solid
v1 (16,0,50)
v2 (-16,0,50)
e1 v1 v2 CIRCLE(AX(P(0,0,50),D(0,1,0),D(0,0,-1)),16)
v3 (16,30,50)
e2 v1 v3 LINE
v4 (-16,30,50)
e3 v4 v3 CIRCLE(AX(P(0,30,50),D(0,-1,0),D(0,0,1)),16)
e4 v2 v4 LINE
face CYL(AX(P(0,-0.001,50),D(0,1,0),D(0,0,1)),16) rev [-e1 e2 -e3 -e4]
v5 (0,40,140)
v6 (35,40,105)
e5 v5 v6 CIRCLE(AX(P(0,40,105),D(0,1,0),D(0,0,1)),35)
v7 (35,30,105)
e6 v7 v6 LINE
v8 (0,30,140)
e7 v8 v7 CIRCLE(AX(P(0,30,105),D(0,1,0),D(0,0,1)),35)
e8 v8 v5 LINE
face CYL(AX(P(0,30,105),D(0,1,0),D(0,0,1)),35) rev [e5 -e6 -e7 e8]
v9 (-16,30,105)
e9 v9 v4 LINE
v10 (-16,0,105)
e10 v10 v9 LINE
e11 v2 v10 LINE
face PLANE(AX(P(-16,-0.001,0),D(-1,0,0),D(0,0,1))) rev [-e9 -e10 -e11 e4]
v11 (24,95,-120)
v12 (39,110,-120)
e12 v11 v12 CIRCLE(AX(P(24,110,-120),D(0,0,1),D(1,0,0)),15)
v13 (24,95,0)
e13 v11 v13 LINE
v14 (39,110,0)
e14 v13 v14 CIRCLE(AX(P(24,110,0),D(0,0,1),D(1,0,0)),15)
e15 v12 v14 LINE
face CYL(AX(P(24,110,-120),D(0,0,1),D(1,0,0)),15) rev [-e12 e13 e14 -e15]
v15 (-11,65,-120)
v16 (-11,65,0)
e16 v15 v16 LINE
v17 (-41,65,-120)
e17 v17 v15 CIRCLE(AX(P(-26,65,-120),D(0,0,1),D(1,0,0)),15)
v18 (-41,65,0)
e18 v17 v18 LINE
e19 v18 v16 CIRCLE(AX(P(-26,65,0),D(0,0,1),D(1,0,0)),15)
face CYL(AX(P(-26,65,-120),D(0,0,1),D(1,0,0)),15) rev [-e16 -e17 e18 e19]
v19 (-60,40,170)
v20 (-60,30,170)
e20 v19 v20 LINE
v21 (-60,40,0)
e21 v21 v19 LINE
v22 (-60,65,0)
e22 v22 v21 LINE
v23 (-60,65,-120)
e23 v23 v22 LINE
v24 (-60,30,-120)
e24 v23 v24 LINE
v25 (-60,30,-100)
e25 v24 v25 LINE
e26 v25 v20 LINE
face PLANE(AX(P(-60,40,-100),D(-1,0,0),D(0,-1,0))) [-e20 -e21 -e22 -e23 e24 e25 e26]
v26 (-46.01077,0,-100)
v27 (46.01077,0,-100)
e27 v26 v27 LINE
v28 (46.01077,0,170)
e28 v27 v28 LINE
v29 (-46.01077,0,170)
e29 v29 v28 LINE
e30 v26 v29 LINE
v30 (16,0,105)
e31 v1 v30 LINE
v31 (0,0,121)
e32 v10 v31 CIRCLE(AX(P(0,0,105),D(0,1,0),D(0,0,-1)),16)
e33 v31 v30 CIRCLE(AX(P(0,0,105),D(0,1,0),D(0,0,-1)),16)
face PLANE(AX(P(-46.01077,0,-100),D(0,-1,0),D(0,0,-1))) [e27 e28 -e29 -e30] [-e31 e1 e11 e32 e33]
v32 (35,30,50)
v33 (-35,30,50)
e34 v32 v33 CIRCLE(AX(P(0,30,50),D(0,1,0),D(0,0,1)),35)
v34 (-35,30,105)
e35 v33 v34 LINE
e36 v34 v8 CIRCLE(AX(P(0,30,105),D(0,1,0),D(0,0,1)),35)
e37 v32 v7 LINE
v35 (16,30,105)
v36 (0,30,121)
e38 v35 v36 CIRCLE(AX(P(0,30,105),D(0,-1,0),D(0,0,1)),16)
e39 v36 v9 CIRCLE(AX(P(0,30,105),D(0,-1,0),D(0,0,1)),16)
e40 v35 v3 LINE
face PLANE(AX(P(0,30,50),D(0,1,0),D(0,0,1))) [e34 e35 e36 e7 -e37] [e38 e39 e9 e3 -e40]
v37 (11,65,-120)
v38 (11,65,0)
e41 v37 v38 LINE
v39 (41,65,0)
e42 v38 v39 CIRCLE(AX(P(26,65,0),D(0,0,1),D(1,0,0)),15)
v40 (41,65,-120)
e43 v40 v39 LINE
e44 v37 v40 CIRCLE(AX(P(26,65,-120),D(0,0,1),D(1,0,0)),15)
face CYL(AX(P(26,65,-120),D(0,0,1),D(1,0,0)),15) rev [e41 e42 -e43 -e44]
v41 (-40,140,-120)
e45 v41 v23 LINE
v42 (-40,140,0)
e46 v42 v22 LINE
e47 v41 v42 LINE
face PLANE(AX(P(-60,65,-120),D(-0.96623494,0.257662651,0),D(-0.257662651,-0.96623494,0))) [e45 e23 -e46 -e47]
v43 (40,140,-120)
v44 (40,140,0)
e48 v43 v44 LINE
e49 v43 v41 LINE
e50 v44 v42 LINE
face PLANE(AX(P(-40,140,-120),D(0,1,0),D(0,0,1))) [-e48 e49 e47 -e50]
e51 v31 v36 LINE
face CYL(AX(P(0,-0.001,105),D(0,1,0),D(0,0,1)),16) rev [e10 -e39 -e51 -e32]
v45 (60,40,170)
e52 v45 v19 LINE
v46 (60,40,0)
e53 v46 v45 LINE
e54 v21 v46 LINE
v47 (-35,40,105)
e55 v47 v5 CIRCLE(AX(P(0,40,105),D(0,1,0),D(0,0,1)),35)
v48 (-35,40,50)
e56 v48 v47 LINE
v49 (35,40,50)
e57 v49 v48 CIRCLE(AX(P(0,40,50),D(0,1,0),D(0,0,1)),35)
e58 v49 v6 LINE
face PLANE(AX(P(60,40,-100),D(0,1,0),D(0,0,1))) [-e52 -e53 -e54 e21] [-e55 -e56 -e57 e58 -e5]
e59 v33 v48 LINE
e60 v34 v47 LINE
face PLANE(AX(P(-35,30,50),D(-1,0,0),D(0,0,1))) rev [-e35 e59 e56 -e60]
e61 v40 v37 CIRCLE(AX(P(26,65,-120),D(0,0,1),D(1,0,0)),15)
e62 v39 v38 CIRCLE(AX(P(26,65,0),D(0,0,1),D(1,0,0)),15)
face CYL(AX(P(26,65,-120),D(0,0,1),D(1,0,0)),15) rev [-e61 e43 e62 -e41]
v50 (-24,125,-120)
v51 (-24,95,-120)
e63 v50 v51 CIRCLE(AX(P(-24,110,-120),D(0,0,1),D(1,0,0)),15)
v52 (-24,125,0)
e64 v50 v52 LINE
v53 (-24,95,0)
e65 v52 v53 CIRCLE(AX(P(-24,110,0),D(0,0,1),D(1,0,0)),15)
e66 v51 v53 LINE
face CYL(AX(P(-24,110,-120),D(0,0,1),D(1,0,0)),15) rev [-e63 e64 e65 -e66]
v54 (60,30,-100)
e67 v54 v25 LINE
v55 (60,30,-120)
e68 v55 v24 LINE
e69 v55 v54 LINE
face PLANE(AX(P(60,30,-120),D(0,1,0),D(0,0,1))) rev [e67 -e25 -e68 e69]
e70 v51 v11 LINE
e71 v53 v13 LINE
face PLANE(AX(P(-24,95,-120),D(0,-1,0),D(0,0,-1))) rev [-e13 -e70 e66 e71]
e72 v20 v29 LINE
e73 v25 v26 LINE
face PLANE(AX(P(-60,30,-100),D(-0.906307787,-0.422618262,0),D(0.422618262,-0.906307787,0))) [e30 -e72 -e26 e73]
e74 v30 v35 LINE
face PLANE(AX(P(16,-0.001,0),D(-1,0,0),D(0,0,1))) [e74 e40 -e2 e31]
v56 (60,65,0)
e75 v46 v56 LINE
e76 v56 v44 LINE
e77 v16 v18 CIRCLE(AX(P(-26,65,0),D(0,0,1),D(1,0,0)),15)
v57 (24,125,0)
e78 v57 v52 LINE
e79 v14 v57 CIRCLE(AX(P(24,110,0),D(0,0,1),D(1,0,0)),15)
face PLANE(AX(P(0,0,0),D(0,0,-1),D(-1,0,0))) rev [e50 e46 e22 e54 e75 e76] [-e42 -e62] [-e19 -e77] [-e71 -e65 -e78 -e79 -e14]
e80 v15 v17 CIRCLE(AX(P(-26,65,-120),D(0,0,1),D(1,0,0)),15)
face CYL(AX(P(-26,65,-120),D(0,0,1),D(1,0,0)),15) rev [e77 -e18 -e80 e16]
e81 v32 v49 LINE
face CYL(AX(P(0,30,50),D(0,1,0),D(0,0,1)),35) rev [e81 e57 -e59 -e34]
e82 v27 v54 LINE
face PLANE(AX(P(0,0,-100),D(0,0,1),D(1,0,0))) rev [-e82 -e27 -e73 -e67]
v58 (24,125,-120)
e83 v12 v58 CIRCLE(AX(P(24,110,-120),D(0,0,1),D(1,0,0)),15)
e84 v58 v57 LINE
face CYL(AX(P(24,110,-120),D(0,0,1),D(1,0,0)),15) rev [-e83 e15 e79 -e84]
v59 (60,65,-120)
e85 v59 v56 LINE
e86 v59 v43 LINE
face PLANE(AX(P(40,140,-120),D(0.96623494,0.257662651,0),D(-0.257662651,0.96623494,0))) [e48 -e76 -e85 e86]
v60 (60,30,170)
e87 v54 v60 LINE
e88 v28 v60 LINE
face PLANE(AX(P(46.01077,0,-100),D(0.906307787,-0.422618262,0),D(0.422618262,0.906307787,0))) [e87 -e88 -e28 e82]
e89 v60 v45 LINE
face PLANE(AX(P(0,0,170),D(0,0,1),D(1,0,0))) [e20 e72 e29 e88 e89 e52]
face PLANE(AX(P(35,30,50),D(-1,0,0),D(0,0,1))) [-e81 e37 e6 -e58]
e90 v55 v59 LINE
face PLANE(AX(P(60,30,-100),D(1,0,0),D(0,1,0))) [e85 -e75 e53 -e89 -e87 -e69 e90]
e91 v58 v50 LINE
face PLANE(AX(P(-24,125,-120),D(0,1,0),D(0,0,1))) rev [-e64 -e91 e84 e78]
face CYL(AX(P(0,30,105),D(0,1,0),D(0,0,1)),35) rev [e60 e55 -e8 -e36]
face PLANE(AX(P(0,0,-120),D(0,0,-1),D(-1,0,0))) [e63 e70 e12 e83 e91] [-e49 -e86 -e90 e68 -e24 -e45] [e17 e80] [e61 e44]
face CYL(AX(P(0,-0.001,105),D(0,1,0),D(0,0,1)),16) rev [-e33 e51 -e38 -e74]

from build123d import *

# Parameters (mm, degrees)
BASE_RAIL_DEPTH                         = 170
BASE_RAIL_DEPTH_BACK                    = 100
UPRIGHT_BLOCK_PROFILE_SKETCH_R          = 15
UPRIGHT_BLOCK_WITH_SLOT_AND_HOLES_DEPTH = 120
UPRIGHT_EXTENSION_SKETCH_W              = 120
UPRIGHT_EXTENSION_SKETCH_H              = 10
UPRIGHT_EXTENSION_BLOCK_DEPTH           = 20
MOUNTING_SLOT_COUNTERBORE_10MM_DEPTH    = 10
MOUNTING_SLOT_THROUGH_REACH             = 208.155


with BuildPart() as part:
    # Base Rail Profile Sketch → Base Rail (new, two sides: drawn at the far end of the back side and taken through both)
    with BuildSketch(Plane.XY.offset(-BASE_RAIL_DEPTH_BACK)):
        Polygon((-46.010770255, 0), (46.010770255, 0), (60, 30), (60, 40), (-60, 40), (-60, 30), align=None)
    extrude(amount=BASE_RAIL_DEPTH + BASE_RAIL_DEPTH_BACK)

    # Upright Block Profile Sketch → Upright Block with Slot and Holes (add)
    with BuildSketch(Plane.XY):
        Polygon((-60, 40), (-60, 65), (-40, 140), (40, 140), (60, 65), (60, 40), align=None)
        with Locations((-26, 65)):
            Circle(UPRIGHT_BLOCK_PROFILE_SKETCH_R, mode=Mode.SUBTRACT)
        with Locations((26, 65)):
            Circle(UPRIGHT_BLOCK_PROFILE_SKETCH_R, mode=Mode.SUBTRACT)
        with BuildLine():
            Line((-24, 125), (24, 125))
            ThreePointArc((24, 125), (39, 110), (24, 95))
            Line((24, 95), (-24, 95))
            ThreePointArc((-24, 95), (-39, 110), (-24, 125))
        make_face(mode=Mode.SUBTRACT)
    extrude(amount=-UPRIGHT_BLOCK_WITH_SLOT_AND_HOLES_DEPTH)

    # Upright Extension Sketch → Upright Extension Block (add)
    with BuildSketch(Plane(origin=(0, 0, -100), x_dir=(-1, 0, 0), z_dir=(0, 0, -1))):
        with Locations((0, 35)):
            Rectangle(UPRIGHT_EXTENSION_SKETCH_W, UPRIGHT_EXTENSION_SKETCH_H)
    extrude(amount=UPRIGHT_EXTENSION_BLOCK_DEPTH)

    # Base Mounting Slot Sketch → Mounting Slot Counterbore 10mm (cut)
    with BuildSketch(Plane(origin=(0, 40, 0), x_dir=(1, 0, 0), z_dir=(0, 1, 0))):
        with BuildLine():
            Line((35, -50), (35, -105))
            ThreePointArc((35, -105), (0, -140), (-35, -105))
            Line((-35, -105), (-35, -50))
            ThreePointArc((-35, -50), (0, -15), (35, -50))
        make_face()
    extrude(amount=-MOUNTING_SLOT_COUNTERBORE_10MM_DEPTH, mode=Mode.SUBTRACT)

    # Sketch4_3 → Mounting Slot Through (cut, up to next)
    with BuildSketch(Plane(origin=(0, 40, 0), x_dir=(1, 0, 0), z_dir=(0, 1, 0)), mode=Mode.PRIVATE) as mounting_slot_through_sk1:
        with BuildLine():
            Line((16, -50), (16, -105))
            ThreePointArc((16, -105), (0, -121), (-16, -105))
            Line((-16, -105), (-16, -50))
            ThreePointArc((-16, -50), (0, -34), (16, -50))
        make_face()
    mounting_slot_through_tool1 = extrude(mounting_slot_through_sk1.sketch, amount=-MOUNTING_SLOT_THROUGH_REACH, mode=Mode.PRIVATE) & part.part
    add(mounting_slot_through_tool1.solids().sort_by_distance((0, 40, 77.5))[0], mode=Mode.SUBTRACT)


solid = part.part
